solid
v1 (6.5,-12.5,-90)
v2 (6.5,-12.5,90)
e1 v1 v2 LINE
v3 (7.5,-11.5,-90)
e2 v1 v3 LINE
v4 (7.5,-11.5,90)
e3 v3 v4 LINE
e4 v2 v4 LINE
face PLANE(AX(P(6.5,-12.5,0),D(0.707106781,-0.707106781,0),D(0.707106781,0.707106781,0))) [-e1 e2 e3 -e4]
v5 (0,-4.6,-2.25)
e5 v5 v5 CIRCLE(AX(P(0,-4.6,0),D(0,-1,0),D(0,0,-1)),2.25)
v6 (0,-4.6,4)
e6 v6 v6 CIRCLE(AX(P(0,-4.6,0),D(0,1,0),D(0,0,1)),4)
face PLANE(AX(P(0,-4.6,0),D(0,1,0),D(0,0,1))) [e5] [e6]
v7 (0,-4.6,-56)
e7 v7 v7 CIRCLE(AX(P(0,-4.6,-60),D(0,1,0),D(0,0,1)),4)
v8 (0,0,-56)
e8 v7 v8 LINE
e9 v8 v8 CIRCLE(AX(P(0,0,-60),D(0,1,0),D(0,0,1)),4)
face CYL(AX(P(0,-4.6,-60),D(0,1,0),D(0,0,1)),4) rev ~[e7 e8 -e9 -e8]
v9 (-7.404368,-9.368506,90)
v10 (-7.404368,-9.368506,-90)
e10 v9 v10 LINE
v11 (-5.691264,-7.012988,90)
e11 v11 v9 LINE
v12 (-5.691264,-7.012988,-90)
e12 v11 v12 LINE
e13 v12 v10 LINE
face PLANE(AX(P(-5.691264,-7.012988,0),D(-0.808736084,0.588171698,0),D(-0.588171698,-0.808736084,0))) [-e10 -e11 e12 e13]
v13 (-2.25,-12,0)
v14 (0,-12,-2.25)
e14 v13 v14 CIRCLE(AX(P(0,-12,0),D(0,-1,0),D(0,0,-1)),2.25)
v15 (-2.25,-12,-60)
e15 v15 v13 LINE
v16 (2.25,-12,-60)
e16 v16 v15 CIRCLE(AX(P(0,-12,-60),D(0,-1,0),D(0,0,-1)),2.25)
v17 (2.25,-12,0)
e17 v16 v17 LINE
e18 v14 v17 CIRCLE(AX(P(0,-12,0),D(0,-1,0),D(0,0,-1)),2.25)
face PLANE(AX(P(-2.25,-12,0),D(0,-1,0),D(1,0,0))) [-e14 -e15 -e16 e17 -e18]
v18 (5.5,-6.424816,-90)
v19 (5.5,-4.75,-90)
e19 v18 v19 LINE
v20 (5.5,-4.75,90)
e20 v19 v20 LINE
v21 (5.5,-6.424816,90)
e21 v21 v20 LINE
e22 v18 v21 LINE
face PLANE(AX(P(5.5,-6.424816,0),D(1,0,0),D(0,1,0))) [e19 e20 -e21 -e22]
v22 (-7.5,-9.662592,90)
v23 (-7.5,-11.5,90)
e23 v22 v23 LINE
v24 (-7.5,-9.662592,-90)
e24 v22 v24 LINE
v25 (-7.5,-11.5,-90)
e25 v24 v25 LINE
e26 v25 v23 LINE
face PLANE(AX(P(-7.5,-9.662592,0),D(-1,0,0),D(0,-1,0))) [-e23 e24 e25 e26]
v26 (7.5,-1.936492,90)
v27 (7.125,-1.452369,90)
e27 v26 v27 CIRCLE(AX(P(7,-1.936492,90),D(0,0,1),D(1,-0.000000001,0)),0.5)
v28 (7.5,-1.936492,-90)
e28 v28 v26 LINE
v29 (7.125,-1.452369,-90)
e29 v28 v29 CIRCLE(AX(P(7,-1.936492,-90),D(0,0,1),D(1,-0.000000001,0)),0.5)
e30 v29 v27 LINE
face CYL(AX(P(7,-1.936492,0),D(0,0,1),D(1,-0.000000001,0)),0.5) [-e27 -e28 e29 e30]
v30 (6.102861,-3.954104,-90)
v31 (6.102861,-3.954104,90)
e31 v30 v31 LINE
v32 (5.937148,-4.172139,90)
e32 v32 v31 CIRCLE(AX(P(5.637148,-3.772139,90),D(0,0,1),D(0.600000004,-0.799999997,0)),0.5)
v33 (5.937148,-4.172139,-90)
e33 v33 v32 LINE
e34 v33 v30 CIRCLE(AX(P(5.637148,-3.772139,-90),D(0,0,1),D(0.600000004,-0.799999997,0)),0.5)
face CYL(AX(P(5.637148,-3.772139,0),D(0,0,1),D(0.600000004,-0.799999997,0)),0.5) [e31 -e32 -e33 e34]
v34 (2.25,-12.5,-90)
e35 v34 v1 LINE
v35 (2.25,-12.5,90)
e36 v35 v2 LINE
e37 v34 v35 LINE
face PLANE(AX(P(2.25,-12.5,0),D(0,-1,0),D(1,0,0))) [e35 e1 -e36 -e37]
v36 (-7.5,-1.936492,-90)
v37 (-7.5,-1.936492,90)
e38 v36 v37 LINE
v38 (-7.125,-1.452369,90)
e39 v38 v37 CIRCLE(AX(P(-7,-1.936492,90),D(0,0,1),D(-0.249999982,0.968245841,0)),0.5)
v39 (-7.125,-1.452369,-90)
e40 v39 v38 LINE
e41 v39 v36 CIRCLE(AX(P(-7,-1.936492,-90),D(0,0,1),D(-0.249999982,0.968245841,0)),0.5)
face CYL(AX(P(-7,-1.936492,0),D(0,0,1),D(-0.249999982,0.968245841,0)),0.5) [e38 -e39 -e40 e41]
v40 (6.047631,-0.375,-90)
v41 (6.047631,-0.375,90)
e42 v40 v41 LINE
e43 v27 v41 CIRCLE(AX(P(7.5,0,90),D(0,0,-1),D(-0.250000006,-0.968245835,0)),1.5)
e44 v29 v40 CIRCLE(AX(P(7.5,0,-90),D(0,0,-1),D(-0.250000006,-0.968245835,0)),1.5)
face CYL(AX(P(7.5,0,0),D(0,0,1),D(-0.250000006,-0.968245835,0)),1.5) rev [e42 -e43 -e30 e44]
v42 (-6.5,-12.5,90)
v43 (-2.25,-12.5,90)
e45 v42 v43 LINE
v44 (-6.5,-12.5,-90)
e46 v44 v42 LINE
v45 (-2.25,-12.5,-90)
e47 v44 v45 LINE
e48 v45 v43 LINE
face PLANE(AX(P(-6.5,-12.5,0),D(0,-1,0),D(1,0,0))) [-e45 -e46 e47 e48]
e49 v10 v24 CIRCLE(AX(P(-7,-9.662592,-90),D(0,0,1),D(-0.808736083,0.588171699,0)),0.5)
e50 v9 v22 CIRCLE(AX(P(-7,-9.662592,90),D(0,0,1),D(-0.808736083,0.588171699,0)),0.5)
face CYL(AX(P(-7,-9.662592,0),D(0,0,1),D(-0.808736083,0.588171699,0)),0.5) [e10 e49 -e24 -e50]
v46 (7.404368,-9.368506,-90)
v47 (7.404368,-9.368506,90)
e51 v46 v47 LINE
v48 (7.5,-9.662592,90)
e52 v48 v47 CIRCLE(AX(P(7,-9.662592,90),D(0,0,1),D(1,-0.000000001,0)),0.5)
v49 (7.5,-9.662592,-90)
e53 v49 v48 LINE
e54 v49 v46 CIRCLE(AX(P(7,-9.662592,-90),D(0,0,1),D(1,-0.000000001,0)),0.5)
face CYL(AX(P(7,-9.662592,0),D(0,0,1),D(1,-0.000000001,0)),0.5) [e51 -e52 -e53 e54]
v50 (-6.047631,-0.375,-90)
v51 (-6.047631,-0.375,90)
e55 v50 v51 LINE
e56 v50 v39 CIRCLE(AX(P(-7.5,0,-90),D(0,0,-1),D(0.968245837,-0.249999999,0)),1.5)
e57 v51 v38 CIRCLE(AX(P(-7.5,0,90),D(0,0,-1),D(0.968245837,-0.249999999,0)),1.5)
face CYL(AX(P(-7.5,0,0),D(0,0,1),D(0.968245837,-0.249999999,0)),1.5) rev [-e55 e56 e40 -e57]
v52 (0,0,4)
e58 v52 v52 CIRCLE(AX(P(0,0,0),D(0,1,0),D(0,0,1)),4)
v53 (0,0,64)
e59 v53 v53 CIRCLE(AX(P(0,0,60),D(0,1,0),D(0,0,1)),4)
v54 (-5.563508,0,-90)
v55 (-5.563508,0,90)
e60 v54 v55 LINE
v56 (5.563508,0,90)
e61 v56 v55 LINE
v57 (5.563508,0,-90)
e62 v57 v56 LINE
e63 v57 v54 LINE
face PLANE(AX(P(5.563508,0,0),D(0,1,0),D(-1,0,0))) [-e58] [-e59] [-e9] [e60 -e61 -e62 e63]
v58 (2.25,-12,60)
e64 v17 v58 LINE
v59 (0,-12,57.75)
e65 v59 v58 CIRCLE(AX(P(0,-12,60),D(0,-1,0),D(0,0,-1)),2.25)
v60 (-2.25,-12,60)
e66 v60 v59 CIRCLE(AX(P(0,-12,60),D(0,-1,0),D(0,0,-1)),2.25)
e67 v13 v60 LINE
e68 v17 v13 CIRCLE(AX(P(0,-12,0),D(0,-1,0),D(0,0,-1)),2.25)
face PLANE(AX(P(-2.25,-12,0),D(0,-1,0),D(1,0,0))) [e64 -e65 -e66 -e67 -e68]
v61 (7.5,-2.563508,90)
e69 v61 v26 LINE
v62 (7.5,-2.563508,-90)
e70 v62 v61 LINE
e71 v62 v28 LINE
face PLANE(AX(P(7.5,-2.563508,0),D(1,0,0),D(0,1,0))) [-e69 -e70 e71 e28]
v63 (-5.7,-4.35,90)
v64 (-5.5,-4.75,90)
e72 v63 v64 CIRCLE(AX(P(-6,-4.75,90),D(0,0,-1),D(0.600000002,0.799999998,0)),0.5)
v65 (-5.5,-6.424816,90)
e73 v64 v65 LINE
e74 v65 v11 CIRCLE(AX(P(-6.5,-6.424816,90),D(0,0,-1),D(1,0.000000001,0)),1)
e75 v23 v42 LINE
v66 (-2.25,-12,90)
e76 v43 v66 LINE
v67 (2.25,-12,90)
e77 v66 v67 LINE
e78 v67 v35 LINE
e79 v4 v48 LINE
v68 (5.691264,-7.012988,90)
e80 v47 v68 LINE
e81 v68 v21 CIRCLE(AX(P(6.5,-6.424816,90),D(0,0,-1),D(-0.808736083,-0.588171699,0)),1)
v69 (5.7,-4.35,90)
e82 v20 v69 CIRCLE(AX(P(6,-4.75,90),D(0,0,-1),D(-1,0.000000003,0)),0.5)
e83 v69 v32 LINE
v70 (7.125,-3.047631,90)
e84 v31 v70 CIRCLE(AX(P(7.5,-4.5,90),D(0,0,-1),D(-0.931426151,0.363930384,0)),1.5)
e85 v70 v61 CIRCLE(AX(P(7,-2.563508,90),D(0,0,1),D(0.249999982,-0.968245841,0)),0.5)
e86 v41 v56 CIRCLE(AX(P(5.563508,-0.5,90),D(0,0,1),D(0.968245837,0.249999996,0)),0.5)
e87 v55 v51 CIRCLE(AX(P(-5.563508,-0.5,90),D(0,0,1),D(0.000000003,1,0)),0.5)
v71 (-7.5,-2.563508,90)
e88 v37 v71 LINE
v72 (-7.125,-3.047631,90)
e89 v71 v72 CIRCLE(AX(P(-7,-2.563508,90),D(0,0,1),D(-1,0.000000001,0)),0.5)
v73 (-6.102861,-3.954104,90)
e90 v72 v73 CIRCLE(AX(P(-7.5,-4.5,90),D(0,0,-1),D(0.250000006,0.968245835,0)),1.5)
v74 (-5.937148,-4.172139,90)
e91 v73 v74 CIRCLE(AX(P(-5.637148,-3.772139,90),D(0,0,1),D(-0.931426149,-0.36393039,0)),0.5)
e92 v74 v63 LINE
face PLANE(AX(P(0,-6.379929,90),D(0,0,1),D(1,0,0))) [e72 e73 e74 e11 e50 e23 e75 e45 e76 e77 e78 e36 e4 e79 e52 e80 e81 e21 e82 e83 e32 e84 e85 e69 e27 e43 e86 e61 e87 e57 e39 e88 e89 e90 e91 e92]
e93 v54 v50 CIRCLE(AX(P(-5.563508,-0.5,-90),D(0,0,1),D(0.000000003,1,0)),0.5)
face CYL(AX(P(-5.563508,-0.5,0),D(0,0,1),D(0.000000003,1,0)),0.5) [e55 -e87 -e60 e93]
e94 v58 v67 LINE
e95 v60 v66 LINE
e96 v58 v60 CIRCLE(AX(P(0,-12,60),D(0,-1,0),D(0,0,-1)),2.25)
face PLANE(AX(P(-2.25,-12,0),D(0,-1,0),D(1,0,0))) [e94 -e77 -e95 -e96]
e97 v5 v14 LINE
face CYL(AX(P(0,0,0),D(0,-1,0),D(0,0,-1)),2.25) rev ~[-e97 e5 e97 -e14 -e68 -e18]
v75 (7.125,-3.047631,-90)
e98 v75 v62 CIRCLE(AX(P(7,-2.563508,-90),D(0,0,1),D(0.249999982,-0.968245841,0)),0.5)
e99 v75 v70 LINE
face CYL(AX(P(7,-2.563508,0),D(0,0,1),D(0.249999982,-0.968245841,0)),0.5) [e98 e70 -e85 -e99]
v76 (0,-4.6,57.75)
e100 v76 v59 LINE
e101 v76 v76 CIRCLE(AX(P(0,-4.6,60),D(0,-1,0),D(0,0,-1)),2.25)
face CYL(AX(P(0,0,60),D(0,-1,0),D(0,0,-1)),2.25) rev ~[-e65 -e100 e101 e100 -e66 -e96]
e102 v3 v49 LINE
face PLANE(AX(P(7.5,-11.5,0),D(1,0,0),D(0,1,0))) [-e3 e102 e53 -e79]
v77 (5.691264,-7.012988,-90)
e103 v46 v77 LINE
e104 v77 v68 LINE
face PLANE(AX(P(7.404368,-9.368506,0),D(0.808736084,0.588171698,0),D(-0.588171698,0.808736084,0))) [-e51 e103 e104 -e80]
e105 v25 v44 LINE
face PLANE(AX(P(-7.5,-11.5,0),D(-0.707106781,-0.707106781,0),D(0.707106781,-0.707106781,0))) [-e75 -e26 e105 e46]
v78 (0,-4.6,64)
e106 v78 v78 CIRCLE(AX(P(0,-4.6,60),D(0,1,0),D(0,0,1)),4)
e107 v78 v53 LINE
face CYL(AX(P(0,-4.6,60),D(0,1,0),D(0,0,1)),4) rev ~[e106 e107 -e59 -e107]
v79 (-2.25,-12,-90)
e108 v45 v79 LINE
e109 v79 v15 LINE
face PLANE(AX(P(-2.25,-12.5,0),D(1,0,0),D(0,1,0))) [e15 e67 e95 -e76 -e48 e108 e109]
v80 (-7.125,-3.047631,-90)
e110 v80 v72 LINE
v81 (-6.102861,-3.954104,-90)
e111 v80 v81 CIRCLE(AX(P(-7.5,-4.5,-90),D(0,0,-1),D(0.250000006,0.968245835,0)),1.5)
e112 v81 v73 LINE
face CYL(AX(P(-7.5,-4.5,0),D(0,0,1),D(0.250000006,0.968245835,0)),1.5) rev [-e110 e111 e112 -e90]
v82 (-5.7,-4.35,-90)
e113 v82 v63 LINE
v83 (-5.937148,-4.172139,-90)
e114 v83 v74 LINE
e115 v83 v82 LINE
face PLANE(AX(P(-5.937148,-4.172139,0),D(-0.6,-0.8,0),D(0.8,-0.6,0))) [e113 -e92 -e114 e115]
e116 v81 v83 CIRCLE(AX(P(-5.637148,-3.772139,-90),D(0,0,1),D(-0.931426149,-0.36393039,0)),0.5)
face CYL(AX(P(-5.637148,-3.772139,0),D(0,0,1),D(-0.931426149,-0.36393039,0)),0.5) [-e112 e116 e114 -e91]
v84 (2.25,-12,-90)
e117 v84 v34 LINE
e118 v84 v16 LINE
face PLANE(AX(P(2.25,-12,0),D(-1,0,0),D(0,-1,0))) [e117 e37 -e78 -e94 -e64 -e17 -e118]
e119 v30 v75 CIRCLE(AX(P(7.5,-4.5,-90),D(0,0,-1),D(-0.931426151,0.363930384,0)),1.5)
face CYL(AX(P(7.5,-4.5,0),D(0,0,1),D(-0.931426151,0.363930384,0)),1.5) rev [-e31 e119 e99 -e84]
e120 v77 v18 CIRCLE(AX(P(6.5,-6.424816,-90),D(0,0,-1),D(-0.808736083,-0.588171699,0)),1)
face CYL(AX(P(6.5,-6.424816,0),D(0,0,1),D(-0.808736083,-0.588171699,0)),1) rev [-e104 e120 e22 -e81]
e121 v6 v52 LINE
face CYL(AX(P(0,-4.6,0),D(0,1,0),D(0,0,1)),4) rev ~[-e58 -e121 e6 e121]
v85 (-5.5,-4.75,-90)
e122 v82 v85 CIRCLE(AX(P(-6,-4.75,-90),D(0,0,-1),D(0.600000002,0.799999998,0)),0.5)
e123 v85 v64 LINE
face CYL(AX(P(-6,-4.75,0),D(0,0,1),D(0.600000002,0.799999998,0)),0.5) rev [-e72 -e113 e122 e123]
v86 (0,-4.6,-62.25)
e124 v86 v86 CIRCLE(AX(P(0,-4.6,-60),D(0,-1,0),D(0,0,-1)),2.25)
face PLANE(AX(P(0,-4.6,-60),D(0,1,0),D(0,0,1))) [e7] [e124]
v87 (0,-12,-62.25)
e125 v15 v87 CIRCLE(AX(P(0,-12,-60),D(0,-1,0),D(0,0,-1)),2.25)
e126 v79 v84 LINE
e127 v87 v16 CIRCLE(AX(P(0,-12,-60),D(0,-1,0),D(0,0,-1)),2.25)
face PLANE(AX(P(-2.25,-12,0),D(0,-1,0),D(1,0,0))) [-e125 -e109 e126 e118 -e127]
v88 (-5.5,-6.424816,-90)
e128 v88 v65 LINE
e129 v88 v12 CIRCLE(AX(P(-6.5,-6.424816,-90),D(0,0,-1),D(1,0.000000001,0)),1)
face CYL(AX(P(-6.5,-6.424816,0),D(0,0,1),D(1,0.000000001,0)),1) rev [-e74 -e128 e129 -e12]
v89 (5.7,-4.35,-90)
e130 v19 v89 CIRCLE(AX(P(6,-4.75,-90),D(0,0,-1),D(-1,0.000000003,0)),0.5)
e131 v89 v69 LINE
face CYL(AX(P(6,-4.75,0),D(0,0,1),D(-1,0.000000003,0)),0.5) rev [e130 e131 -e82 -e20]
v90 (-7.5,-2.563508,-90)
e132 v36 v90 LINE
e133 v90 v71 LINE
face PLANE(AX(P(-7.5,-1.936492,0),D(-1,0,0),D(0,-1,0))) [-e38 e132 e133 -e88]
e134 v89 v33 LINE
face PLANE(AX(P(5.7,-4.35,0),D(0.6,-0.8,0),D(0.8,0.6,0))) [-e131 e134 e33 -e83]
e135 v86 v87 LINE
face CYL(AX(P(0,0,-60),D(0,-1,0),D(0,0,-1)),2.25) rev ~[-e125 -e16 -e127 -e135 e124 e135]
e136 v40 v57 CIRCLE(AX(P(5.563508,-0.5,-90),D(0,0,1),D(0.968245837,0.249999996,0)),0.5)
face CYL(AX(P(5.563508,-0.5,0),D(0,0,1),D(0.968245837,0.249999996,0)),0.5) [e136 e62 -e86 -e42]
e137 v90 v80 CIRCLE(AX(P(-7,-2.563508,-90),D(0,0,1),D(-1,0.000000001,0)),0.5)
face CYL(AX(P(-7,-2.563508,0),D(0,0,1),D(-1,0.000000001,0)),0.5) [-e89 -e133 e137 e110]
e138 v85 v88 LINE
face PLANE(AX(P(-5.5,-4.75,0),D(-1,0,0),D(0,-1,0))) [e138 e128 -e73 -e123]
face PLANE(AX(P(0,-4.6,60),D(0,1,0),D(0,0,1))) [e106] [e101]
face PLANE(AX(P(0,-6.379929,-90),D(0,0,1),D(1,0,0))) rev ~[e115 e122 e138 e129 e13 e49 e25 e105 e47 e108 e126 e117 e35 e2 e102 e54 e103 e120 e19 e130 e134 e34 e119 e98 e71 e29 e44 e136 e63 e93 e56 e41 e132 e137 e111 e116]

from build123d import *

# Parameters (mm, degrees)
EXTRUDE_1_DEPTH           = 90
HOLE_WIZARD_1_D           = 4.5
HOLE_WIZARD_1_CBORE_D     = 8
HOLE_WIZARD_1_CBORE_DEPTH = 4.6
PATTERN_LINEAR_2_COUNT    = 3
PATTERN_LINEAR_2_PITCH    = 60


with BuildPart() as part:
    # 草图1 → 凸台-拉伸1 (new, symmetric)
    with BuildSketch(Plane.XY):
        with BuildLine():
            Line((-7.5, -9.662591907), (-7.5, -11.5))
            Line((-7.5, -11.5), (-6.5, -12.5))
            Line((-6.5, -12.5), (-2.25, -12.5))
            Line((-2.25, -12.5), (-2.25, -12))
            Line((-2.25, -12), (2.25, -12))
            Line((2.25, -12), (2.25, -12.5))
            Line((2.25, -12.5), (6.5, -12.5))
            Line((6.5, -12.5), (7.5, -11.5))
            Line((7.5, -11.5), (7.5, -9.662591907))
            ThreePointArc((7.5, -9.662591907), (7.475491336, -9.507969821), (7.404368042, -9.368506058))
            Line((7.404368042, -9.368506058), (5.691263916, -7.012987884))
            ThreePointArc((5.691263916, -7.012987884), (5.549017328, -6.734060358), (5.5, -6.424816186))
            Line((5.5, -6.424816186), (5.5, -4.75))
            ThreePointArc((5.5, -4.75), (5.552786405, -4.526393202), (5.7, -4.35))
            Line((5.7, -4.35), (5.9371477, -4.172139225))
            ThreePointArc((5.9371477, -4.172139225), (6.03522297, -4.074688525), (6.102860772, -3.954104425))
            ThreePointArc((6.102860772, -3.954104425), (6.504739846, -3.377744581), (7.12499999, -3.047631248))
            ThreePointArc((7.12499999, -3.047631248), (7.395284704, -2.869694549), (7.5, -2.563508327))
            Line((7.5, -2.563508327), (7.5, -1.936491673))
            ThreePointArc((7.5, -1.936491673), (7.395284705, -1.630305452), (7.124999991, -1.452368753))
            ThreePointArc((7.124999991, -1.452368753), (6.439339825, -1.060660169), (6.047631245, -0.375))
            ThreePointArc((6.047631245, -0.375), (5.869694545, -0.104715292), (5.563508327, 0))
            Line((5.563508327, 0), (-5.563508327, 0))
            ThreePointArc((-5.563508327, 0), (-5.869694545, -0.104715292), (-6.047631245, -0.375))
            ThreePointArc((-6.047631245, -0.375), (-6.439339824, -1.060660168), (-7.12499999, -1.452368752))
            ThreePointArc((-7.12499999, -1.452368752), (-7.395284704, -1.630305451), (-7.5, -1.936491673))
            Line((-7.5, -1.936491673), (-7.5, -2.563508327))
            ThreePointArc((-7.5, -2.563508327), (-7.395284705, -2.869694548), (-7.124999991, -3.047631247))
            ThreePointArc((-7.124999991, -3.047631247), (-6.504739849, -3.377744578), (-6.102860775, -3.954104419))
            ThreePointArc((-6.102860775, -3.954104419), (-6.035222972, -4.074688523), (-5.9371477, -4.172139225))
            Line((-5.9371477, -4.172139225), (-5.7, -4.35))
            ThreePointArc((-5.7, -4.35), (-5.552786405, -4.526393202), (-5.5, -4.75))
            Line((-5.5, -4.75), (-5.5, -6.424816186))
            ThreePointArc((-5.5, -6.424816186), (-5.549017328, -6.734060358), (-5.691263916, -7.012987884))
            Line((-5.691263916, -7.012987884), (-7.404368042, -9.368506058))
            ThreePointArc((-7.404368042, -9.368506058), (-7.475491336, -9.507969821), (-7.5, -9.662591907))
        make_face()
    extrude(amount=EXTRUDE_1_DEPTH, both=True)

    # 打孔尺寸(%根据)内六角圆柱头螺钉的类型1 (through all)
    with Locations(Plane(origin=(0, 0, -60), x_dir=(0, 0, 1), z_dir=(0, 1, 0))):
        with Locations((0, 0)):
            hole_wizard_1 = CounterBoreHole(HOLE_WIZARD_1_D / 2, HOLE_WIZARD_1_CBORE_D / 2, HOLE_WIZARD_1_CBORE_DEPTH)

    # 阵列(线性)2: 打孔尺寸(%根据)内六角圆柱头螺钉的类型1 ×3
    with Locations(*[(0, 0, i * PATTERN_LINEAR_2_PITCH) for i in range(1, PATTERN_LINEAR_2_COUNT)]):
        add(hole_wizard_1, mode=Mode.SUBTRACT)


solid = part.part
